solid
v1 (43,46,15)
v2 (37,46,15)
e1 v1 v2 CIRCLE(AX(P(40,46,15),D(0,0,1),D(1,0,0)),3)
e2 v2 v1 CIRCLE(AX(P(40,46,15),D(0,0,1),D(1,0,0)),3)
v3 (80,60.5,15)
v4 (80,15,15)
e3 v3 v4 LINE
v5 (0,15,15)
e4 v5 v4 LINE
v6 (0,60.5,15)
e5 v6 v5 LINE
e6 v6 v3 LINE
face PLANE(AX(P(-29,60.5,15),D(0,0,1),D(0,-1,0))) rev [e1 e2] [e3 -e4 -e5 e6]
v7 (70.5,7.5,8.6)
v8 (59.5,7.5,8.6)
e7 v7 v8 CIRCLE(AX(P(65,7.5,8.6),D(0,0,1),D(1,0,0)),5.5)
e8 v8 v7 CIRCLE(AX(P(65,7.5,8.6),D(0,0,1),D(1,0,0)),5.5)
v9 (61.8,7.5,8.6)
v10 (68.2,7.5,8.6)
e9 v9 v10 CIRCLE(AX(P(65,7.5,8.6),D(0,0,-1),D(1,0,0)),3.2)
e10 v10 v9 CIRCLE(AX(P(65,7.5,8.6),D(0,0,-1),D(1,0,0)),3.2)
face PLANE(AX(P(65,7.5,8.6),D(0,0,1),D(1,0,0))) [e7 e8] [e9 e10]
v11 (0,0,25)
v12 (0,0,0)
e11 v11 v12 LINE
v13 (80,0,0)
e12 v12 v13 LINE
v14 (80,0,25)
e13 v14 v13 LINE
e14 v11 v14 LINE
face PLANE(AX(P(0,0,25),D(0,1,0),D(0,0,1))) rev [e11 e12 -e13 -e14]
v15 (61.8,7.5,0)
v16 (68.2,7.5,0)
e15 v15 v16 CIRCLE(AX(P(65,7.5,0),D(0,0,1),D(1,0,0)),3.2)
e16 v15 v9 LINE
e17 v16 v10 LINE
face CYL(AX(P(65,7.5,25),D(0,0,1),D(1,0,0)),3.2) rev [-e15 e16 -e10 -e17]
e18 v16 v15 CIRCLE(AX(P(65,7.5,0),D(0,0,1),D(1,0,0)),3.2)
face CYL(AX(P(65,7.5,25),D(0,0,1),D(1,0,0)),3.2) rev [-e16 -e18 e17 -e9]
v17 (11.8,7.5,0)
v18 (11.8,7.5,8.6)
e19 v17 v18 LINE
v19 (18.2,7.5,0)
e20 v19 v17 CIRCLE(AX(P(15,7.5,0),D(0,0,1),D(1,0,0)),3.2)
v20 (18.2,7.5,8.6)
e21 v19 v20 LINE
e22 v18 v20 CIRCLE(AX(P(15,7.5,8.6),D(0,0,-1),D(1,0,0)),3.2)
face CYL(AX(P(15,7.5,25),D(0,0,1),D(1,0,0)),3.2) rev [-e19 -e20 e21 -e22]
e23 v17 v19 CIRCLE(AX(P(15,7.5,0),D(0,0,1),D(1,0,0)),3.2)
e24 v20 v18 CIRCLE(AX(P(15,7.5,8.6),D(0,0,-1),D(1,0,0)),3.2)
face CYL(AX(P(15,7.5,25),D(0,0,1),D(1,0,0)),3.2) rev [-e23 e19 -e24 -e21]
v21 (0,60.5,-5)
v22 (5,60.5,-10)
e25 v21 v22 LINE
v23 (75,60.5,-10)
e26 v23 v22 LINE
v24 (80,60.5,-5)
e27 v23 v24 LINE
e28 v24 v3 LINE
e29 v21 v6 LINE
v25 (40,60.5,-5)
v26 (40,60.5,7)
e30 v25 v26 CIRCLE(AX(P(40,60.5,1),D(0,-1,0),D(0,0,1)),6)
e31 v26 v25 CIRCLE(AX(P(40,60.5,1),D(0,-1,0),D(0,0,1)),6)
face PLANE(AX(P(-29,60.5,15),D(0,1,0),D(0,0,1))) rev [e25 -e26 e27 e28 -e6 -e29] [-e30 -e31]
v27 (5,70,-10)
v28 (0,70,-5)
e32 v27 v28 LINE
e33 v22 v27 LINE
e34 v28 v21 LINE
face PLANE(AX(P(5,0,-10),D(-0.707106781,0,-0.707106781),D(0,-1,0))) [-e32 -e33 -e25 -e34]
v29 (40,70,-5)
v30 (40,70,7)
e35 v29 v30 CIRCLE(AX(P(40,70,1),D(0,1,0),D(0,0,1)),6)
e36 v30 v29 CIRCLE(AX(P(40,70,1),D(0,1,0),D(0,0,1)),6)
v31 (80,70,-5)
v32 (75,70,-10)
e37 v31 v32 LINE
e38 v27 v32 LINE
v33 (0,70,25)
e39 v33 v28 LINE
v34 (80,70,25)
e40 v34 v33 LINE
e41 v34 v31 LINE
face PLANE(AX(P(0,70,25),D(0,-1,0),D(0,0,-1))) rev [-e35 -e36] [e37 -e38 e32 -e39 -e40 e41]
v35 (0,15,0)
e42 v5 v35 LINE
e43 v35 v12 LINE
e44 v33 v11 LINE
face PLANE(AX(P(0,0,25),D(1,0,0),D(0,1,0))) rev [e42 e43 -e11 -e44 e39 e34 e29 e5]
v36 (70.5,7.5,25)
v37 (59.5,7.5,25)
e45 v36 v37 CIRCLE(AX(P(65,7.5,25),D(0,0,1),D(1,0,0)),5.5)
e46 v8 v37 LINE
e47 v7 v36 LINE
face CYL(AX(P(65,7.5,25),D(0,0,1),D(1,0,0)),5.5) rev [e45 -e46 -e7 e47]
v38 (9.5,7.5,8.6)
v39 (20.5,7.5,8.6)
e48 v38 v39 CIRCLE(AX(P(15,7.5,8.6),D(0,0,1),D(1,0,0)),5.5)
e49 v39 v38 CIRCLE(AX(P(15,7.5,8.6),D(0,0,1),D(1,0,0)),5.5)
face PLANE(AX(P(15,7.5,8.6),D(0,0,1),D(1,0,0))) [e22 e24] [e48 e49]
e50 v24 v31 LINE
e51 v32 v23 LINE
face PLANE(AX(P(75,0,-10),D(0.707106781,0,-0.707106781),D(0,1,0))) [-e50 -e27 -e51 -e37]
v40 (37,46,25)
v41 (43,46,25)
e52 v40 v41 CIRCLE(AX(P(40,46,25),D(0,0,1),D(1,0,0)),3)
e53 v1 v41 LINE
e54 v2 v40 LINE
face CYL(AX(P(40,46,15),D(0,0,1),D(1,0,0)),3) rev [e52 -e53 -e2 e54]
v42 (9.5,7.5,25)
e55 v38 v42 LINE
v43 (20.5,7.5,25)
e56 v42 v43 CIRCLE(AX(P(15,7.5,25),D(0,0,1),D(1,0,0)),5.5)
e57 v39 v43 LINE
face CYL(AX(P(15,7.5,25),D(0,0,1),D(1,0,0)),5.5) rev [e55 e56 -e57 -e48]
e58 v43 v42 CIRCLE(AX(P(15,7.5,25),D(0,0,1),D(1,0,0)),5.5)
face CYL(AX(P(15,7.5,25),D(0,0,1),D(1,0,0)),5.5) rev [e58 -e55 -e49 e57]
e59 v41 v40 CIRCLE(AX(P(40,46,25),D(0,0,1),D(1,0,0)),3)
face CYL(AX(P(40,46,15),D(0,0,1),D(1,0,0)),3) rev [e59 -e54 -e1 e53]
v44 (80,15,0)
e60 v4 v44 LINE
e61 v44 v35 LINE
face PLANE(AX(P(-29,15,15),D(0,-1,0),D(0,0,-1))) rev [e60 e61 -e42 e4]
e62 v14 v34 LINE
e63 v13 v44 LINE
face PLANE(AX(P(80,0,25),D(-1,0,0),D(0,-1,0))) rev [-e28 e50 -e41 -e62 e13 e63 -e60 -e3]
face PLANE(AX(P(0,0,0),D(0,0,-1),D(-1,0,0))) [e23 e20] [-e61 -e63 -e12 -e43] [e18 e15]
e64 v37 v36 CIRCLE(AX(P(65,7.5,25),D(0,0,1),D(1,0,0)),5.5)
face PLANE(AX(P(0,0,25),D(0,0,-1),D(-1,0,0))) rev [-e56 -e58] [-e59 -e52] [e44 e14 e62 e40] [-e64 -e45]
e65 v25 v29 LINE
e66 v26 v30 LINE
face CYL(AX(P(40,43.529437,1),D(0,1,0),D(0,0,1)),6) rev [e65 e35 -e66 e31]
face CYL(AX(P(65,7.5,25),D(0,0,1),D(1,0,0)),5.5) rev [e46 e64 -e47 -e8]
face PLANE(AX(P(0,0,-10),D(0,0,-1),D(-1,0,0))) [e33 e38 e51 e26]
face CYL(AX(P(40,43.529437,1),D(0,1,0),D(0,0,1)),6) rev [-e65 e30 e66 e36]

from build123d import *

# Parameters (mm, degrees)
SKETCH_1_W                   = 80
SKETCH_1_H                   = 70
EXTRUDE_1_DEPTH              = 25
SKETCH_2_W                   = 15
SKETCH_2_H                   = 45.5
CUT_EXTRUDE_1_DEPTH          = 109
HOLE_WIZARD_M6_1_D           = 6.4
HOLE_WIZARD_M6_1_CBORE_D     = 11
HOLE_WIZARD_M6_1_CBORE_DEPTH = 6.4
SKETCH_7_R                   = 5.5
CUT_EXTRUDE_3_DEPTH          = 10
SKETCH_8_R                   = 3
CUT_EXTRUDE_4_DEPTH          = 10
SKETCH_9_W                   = 80
SKETCH_9_H                   = 9.5
EXTRUDE_2_DEPTH              = 10
SKETCH_10_R                  = 6
CUT_EXTRUDE_5_DEPTH          = 9.5
CHAMFER_1_SIZE               = 5


with BuildPart() as part:
    # 草图1 → 凸台-拉伸1 (new body)
    with BuildSketch(Plane.XY):
        with Locations((40, 35)):
            Rectangle(SKETCH_1_W, SKETCH_1_H)
    extrude(amount=EXTRUDE_1_DEPTH)

    # 草图2 → 切除-拉伸1 (cut)
    with BuildSketch(Plane(origin=(80, 0, 0), x_dir=(0, 0, -1), z_dir=(1, 0, 0))):
        with Locations((-7.5, 37.75)):
            Rectangle(SKETCH_2_W, SKETCH_2_H)
    extrude(amount=-CUT_EXTRUDE_1_DEPTH, mode=Mode.SUBTRACT)

    # M6 六角凹头螺钉的柱形沉头孔1 (through all)
    with Locations(Plane.XY.offset(25)):
        with Locations((15, 7.5), (65, 7.5)):
            CounterBoreHole(HOLE_WIZARD_M6_1_D / 2, HOLE_WIZARD_M6_1_CBORE_D / 2, HOLE_WIZARD_M6_1_CBORE_DEPTH)

    # 草图7 → 切除-拉伸3 (cut)
    with BuildSketch(Plane.XY.offset(18.6)):
        with Locations((15, 7.5)):
            Circle(SKETCH_7_R)
        with Locations((65, 7.5)):
            Circle(SKETCH_7_R)
    extrude(amount=-CUT_EXTRUDE_3_DEPTH, mode=Mode.SUBTRACT)

    # 草图8 → 切除-拉伸4 (cut)
    with BuildSketch(Plane.XY.offset(25)):
        with Locations((40, 46)):
            Circle(SKETCH_8_R)
    extrude(amount=-CUT_EXTRUDE_4_DEPTH, mode=Mode.SUBTRACT)

    # 草图9 → 凸台-拉伸2 (add)
    with BuildSketch(Plane(origin=(0, 0, 0), x_dir=(-1, 0, 0), z_dir=(0, 0, -1))):
        with Locations((-40, 65.25)):
            Rectangle(SKETCH_9_W, SKETCH_9_H)
    extrude(amount=EXTRUDE_2_DEPTH)

    # 草图10 → 切除-拉伸5 (cut)
    with BuildSketch(Plane(origin=(0, 70, 0), x_dir=(1, 0, 0), z_dir=(0, 1, 0))):
        with Locations(Location((40, -1, 0), (0, 0, 270))):
            Circle(SKETCH_10_R)
    extrude(amount=-CUT_EXTRUDE_5_DEPTH, mode=Mode.SUBTRACT)

    # 倒角1
    chamfer_1_edges = [part.edges().sort_by_distance(p)[0] for p in [
        (80, 65.25, -10),
        (0, 65.25, -10),
    ]]
    chamfer(chamfer_1_edges, length=CHAMFER_1_SIZE)


solid = part.part
